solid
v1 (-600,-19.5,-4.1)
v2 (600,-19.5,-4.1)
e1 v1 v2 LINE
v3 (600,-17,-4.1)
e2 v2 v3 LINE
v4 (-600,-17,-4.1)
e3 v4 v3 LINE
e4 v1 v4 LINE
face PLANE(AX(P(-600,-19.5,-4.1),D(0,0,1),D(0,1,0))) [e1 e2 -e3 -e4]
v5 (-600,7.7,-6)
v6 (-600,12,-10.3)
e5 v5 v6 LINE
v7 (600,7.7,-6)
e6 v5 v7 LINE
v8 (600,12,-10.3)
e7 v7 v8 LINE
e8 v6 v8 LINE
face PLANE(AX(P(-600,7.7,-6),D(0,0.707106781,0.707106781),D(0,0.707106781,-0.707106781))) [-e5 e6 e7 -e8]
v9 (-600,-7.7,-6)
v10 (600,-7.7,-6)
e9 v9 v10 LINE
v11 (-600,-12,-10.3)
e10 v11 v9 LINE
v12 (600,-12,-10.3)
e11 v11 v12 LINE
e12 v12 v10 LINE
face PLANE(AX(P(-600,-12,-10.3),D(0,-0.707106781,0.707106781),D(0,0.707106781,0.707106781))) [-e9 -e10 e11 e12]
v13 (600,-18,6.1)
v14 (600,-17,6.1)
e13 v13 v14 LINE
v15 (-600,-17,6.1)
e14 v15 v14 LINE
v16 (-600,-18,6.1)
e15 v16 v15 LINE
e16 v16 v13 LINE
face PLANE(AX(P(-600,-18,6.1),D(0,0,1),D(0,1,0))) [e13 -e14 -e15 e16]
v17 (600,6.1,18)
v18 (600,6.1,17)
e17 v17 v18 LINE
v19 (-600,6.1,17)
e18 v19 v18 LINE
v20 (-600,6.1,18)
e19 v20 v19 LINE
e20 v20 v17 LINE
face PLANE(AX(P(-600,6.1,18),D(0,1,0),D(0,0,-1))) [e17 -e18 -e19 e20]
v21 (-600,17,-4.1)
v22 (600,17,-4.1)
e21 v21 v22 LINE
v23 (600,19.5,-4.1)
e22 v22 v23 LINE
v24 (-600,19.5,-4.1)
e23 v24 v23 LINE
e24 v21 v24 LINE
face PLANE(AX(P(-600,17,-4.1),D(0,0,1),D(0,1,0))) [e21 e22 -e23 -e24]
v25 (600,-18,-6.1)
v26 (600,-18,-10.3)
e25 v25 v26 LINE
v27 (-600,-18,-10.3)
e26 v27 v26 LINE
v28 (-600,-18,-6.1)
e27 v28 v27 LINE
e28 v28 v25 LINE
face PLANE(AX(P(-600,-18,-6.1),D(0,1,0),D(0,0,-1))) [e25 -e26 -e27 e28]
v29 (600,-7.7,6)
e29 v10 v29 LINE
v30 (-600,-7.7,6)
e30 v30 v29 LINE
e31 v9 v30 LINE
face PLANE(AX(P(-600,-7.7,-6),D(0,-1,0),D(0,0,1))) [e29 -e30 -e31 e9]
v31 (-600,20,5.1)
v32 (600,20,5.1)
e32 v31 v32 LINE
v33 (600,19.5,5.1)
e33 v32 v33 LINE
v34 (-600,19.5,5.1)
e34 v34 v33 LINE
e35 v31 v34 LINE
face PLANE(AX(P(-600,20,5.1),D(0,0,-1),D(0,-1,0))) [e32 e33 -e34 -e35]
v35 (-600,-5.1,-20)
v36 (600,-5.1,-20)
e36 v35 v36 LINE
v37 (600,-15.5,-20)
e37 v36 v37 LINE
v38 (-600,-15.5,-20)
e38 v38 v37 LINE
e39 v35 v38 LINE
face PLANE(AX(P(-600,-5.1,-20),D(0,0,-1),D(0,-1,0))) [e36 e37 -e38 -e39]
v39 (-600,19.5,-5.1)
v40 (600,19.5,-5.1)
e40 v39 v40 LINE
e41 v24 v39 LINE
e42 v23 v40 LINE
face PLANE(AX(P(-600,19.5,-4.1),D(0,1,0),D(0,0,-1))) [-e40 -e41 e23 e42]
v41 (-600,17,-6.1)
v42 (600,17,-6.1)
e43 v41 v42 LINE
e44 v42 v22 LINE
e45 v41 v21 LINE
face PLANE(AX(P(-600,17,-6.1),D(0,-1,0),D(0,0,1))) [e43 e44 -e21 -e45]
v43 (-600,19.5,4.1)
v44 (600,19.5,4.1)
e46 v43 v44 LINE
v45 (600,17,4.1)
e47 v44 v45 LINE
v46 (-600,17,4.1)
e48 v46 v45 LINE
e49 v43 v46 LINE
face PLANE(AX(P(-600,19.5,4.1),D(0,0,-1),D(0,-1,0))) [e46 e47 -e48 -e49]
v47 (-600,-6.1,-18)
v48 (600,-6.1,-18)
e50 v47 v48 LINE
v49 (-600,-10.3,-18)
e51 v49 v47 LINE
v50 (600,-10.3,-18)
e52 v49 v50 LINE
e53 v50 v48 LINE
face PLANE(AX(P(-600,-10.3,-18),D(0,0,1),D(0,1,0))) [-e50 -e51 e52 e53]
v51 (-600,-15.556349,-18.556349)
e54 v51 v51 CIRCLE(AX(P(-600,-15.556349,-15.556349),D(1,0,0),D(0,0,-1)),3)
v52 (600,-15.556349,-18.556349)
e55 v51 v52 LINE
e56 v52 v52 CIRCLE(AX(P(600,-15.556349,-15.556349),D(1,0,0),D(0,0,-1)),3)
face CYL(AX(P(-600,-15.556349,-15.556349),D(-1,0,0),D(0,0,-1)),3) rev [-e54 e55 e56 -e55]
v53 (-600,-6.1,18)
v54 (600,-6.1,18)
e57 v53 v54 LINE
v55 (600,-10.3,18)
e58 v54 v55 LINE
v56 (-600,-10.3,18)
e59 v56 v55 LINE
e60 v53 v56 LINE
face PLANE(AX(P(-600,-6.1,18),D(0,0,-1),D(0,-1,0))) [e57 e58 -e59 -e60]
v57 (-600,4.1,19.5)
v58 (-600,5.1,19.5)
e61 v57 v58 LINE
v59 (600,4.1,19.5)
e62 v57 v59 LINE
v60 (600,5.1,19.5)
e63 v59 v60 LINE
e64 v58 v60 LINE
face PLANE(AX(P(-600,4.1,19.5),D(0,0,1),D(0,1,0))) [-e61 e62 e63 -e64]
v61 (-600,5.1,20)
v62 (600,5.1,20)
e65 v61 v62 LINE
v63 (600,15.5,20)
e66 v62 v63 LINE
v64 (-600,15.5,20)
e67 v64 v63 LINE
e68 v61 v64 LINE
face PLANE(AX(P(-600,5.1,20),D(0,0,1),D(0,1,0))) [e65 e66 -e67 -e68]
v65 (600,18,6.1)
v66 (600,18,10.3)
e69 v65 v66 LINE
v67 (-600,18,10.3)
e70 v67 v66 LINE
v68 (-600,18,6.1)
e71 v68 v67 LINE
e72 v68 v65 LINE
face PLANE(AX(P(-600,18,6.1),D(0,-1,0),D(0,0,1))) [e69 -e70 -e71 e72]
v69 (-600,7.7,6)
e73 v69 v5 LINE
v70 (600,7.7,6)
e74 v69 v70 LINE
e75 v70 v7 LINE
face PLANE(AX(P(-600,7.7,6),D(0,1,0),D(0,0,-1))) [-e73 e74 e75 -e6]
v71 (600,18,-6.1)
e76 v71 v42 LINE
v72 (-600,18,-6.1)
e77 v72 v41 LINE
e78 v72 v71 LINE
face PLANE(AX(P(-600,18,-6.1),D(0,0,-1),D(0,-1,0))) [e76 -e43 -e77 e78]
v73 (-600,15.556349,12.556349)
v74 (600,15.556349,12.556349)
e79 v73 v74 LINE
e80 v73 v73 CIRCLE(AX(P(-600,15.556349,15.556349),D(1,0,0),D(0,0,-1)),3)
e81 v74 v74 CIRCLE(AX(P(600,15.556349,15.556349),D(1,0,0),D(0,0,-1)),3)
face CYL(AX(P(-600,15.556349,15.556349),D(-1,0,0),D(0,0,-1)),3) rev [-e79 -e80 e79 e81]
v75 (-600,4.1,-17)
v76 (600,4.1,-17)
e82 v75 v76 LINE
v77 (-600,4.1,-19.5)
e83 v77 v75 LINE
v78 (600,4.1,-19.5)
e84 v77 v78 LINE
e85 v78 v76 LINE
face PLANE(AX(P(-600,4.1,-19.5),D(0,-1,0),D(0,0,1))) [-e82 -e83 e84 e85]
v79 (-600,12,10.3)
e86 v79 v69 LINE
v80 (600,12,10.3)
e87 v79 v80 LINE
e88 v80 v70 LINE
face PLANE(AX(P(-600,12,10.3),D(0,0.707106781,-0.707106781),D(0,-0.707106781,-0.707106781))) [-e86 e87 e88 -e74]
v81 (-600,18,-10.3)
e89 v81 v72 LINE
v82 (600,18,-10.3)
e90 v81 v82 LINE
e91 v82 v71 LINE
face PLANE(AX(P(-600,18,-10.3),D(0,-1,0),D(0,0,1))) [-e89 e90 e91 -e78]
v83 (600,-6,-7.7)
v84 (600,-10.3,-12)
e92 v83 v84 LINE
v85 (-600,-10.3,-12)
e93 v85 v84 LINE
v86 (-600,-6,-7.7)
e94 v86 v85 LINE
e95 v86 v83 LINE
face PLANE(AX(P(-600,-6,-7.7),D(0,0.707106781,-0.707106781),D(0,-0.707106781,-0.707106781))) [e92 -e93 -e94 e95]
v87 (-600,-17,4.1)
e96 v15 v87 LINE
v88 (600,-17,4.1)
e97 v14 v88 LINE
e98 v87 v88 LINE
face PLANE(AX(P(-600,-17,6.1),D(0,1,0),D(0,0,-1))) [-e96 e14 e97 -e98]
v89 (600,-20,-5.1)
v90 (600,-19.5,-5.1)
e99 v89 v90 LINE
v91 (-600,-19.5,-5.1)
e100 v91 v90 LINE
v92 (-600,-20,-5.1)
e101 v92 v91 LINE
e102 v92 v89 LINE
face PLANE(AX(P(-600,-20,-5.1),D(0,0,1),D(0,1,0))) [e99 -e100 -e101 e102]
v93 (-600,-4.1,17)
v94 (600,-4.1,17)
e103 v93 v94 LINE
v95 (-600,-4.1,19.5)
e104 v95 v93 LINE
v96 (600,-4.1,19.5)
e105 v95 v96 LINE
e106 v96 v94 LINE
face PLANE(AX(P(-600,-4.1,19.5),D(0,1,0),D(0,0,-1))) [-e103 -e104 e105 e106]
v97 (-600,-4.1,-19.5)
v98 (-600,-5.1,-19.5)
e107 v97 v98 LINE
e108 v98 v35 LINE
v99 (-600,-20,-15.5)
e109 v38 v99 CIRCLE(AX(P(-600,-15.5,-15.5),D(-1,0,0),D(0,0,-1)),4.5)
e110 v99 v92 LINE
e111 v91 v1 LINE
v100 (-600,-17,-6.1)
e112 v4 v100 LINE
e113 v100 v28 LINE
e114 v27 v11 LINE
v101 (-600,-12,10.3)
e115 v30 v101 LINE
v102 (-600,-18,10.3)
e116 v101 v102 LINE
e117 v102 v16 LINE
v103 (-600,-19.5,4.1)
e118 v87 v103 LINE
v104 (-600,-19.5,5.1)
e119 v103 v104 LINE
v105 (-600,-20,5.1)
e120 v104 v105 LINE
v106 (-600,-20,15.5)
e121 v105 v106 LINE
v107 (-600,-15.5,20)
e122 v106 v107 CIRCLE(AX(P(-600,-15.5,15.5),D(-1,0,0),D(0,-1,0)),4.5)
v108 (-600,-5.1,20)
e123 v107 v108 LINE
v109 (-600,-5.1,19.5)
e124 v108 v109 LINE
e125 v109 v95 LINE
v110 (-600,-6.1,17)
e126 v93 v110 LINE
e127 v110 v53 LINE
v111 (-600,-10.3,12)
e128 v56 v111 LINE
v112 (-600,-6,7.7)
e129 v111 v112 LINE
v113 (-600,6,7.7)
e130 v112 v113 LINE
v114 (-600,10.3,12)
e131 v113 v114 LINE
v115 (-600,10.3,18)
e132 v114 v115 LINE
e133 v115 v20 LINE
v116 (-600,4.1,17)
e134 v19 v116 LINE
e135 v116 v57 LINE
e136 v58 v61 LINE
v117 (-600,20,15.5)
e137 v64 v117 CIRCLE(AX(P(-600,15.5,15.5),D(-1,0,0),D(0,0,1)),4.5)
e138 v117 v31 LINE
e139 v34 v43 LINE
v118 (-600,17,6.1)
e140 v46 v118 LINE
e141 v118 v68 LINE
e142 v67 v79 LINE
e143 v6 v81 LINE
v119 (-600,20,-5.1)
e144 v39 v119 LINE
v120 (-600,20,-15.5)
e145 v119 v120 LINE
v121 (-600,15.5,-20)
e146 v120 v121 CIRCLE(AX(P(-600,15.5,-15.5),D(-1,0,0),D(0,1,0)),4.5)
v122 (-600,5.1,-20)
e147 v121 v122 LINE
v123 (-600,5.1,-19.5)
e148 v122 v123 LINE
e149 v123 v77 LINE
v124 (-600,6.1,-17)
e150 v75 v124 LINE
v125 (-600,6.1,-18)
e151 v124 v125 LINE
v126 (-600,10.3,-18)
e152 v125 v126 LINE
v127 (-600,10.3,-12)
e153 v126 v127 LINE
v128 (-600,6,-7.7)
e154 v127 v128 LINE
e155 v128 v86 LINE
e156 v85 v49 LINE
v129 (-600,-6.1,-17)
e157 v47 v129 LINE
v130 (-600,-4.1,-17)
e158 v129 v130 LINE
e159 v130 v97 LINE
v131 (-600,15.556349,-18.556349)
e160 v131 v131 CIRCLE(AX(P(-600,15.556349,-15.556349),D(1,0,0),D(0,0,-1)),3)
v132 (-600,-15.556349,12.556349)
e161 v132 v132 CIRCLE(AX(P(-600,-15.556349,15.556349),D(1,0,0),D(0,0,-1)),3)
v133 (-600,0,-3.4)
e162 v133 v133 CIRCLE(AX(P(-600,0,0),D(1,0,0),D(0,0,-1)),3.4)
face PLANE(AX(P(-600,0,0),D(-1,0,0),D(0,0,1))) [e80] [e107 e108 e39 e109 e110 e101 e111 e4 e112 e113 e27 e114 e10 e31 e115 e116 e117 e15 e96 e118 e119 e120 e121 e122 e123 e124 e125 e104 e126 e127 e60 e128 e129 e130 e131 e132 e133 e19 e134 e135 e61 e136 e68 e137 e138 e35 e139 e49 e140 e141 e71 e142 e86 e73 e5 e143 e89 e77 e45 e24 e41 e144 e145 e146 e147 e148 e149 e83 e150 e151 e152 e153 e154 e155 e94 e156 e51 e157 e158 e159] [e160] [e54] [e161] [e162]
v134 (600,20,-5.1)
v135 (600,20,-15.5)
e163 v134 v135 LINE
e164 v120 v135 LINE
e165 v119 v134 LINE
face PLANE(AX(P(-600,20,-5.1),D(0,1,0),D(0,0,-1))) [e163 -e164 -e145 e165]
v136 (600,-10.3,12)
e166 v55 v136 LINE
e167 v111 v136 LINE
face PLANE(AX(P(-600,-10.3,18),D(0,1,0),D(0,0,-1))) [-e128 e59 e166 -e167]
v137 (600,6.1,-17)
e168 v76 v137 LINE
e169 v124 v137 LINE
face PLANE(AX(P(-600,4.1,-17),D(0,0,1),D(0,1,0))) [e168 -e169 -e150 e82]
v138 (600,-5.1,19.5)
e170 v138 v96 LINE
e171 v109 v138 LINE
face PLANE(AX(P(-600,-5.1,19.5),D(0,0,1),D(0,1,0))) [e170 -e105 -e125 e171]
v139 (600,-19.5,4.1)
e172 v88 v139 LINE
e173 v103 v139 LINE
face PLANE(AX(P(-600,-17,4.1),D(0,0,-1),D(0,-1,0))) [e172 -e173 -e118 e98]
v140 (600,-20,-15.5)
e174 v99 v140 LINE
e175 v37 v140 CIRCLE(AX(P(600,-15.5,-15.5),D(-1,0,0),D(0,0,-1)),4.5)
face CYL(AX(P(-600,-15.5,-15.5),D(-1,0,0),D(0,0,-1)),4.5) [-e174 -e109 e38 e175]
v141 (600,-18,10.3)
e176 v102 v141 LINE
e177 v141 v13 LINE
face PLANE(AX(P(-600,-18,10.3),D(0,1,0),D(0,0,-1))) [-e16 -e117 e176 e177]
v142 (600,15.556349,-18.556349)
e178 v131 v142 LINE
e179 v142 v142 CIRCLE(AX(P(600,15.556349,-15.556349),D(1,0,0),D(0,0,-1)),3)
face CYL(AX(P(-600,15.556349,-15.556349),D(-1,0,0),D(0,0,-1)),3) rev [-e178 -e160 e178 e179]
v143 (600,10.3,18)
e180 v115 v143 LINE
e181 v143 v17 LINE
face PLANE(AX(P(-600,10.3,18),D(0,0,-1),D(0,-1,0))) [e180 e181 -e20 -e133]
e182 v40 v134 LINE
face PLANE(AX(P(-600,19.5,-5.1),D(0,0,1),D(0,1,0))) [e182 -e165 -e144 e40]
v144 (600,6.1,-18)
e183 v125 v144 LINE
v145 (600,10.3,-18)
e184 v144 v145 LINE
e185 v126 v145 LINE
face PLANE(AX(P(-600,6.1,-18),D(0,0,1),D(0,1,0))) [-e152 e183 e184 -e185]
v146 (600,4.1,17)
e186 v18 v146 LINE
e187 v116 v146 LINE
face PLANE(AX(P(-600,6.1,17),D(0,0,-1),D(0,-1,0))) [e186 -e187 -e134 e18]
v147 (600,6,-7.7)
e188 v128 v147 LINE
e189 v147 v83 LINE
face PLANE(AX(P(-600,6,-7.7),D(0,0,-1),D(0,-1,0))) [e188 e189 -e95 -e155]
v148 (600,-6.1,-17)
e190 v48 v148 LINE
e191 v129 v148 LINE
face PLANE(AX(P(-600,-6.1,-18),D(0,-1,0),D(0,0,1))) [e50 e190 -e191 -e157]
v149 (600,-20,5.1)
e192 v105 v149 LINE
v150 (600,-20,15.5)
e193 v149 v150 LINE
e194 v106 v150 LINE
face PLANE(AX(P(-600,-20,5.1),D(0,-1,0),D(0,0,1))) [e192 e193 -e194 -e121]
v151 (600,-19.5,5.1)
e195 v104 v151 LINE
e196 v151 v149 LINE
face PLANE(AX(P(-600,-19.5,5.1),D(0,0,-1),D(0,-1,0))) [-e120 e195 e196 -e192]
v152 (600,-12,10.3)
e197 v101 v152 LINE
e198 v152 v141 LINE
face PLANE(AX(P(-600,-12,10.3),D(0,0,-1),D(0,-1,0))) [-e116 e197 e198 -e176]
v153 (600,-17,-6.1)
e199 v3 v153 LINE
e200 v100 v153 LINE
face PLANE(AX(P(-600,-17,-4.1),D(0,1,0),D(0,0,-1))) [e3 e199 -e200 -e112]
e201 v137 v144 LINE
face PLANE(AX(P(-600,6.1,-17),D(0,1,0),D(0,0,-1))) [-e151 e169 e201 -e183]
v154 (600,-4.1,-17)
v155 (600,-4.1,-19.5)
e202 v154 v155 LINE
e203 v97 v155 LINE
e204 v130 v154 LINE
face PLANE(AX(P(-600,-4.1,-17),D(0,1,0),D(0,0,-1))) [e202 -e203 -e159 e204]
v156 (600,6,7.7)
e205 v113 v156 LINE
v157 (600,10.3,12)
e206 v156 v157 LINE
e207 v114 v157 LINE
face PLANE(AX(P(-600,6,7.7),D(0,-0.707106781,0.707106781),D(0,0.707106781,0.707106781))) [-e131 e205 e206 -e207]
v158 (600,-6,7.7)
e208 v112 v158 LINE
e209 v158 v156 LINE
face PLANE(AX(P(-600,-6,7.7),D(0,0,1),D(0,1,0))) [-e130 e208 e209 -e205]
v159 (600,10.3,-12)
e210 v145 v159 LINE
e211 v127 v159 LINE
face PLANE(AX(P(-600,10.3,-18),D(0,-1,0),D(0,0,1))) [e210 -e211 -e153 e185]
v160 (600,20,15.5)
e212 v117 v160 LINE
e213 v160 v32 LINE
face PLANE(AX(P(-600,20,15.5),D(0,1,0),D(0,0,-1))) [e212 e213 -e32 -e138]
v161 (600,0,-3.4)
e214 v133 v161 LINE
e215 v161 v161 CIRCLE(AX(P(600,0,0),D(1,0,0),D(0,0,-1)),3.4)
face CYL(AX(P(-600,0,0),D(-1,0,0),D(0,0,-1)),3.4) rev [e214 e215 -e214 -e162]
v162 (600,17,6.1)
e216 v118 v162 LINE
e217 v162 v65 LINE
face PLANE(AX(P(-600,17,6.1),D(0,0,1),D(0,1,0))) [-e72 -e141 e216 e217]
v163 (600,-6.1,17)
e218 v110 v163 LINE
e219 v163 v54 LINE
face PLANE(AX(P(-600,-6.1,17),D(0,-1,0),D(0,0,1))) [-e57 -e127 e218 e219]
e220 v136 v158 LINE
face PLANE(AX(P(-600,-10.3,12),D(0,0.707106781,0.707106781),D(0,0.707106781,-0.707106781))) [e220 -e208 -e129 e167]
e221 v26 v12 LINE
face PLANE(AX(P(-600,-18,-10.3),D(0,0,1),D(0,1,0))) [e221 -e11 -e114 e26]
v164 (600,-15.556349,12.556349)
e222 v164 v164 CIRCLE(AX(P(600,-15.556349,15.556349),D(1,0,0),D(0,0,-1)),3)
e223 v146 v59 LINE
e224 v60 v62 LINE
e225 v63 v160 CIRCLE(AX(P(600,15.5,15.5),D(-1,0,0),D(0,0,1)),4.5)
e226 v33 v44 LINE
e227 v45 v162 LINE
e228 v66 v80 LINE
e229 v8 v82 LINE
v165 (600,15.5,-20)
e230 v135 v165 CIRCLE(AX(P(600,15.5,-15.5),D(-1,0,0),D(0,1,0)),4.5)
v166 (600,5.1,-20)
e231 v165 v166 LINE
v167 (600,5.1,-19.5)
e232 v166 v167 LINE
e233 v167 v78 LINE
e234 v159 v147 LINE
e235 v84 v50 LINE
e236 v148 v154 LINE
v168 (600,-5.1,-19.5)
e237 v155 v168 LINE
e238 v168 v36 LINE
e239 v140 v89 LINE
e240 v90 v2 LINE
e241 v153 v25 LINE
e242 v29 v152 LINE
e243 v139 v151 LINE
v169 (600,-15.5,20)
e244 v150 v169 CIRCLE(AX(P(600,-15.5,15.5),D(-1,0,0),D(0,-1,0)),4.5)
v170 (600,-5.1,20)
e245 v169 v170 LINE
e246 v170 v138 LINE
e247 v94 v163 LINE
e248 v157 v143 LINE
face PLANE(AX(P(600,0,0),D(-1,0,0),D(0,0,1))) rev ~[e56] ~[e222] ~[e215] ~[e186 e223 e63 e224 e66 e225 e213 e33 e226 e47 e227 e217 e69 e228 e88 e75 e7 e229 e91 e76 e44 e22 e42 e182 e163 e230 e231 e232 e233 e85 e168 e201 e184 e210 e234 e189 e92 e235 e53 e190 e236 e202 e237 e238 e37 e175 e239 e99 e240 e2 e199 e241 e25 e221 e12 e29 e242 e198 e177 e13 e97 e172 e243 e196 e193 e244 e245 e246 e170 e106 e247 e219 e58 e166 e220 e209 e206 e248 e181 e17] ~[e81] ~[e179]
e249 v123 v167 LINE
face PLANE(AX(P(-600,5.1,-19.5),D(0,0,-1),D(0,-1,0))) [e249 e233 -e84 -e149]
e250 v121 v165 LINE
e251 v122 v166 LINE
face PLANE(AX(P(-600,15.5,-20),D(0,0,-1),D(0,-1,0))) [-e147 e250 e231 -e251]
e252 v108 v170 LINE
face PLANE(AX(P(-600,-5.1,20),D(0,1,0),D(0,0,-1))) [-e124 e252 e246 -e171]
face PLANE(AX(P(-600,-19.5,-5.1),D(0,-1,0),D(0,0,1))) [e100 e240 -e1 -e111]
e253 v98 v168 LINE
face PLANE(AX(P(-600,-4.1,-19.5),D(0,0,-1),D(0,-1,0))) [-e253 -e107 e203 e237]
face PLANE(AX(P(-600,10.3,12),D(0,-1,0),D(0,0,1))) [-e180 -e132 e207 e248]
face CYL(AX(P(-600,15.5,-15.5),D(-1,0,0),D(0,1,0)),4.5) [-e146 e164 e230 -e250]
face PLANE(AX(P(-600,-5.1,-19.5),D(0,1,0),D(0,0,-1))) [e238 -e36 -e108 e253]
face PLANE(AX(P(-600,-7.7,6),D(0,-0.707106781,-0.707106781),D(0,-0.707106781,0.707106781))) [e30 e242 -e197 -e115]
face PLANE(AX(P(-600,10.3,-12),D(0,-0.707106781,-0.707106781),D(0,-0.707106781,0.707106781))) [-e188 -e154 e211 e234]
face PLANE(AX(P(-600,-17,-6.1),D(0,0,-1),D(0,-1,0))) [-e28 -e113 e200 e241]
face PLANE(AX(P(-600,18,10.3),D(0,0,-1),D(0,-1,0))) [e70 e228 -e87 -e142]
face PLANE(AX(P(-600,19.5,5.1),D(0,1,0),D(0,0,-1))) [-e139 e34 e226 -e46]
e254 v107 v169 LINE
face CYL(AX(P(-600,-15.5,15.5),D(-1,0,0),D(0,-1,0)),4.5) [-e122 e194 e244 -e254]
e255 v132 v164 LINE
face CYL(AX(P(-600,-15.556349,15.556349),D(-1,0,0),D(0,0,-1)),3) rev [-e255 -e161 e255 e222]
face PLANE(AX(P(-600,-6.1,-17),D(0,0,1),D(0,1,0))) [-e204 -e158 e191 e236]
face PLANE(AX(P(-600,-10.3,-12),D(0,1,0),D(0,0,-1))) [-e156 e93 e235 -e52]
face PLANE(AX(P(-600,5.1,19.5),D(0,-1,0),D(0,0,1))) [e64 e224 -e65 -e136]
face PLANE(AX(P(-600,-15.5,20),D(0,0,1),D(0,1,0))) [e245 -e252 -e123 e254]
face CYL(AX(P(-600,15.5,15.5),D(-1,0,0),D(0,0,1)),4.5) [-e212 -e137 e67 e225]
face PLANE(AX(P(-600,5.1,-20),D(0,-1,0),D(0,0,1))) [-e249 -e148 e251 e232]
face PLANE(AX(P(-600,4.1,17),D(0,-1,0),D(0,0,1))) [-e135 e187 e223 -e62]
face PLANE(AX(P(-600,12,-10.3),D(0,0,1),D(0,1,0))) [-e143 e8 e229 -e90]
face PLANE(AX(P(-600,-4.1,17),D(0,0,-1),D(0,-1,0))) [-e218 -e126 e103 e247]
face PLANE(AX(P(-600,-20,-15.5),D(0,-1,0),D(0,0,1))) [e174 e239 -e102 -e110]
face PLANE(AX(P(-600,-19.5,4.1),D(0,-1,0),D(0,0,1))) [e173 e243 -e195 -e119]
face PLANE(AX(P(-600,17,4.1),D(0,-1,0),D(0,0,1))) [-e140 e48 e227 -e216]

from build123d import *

# Parameters (mm, degrees)
SKETCH1_R                 = 3.4
SKETCH1_R_2               = 3
F_40_X_40W_X_R4_5_1_DEPTH = 1200


with BuildPart() as part:
    # Sketch1 → 铝型材 40 X 40W X R4.5(1) (new body)
    with BuildSketch(Plane(origin=(-600, 0, 0), x_dir=(0, 0, -1), z_dir=(1, 0, 0))):
        with BuildLine():
            Line((-5.1, 20), (-5.1, 19.5))
            Line((-5.1, 19.5), (-4.1, 19.5))
            Line((-4.1, 19.5), (-4.1, 17))
            Line((-4.1, 17), (-6.1, 17))
            Line((-6.1, 17), (-6.1, 18))
            Line((-6.1, 18), (-10.3, 18))
            Line((-10.3, 18), (-10.3, 12))
            Line((-10.3, 12), (-6, 7.7))
            Line((-6, 7.7), (6, 7.7))
            Line((6, 7.7), (10.3, 12))
            Line((10.3, 12), (10.3, 18))
            Line((10.3, 18), (6.1, 18))
            Line((6.1, 18), (6.1, 17))
            Line((6.1, 17), (4.1, 17))
            Line((4.1, 17), (4.1, 19.5))
            Line((4.1, 19.5), (5.1, 19.5))
            Line((5.1, 19.5), (5.1, 20))
            Line((5.1, 20), (15.5, 20))
            ThreePointArc((15.5, 20), (18.681980515, 18.681980515), (20, 15.5))
            Line((20, 15.5), (20, 5.1))
            Line((20, 5.1), (19.5, 5.1))
            Line((19.5, 5.1), (19.5, 4.1))
            Line((19.5, 4.1), (17, 4.1))
            Line((17, 4.1), (17, 6.1))
            Line((17, 6.1), (18, 6.1))
            Line((18, 6.1), (18, 10.3))
            Line((18, 10.3), (12, 10.3))
            Line((12, 10.3), (7.7, 6))
            Line((7.7, 6), (7.7, -6))
            Line((7.7, -6), (12, -10.3))
            Line((12, -10.3), (18, -10.3))
            Line((18, -10.3), (18, -6.1))
            Line((18, -6.1), (17, -6.1))
            Line((17, -6.1), (17, -4.1))
            Line((17, -4.1), (19.5, -4.1))
            Line((19.5, -4.1), (19.5, -5.1))
            Line((19.5, -5.1), (20, -5.1))
            Line((20, -5.1), (20, -15.5))
            ThreePointArc((20, -15.5), (18.681980515, -18.681980515), (15.5, -20))
            Line((15.5, -20), (5.1, -20))
            Line((5.1, -20), (5.1, -19.5))
            Line((5.1, -19.5), (4.1, -19.5))
            Line((4.1, -19.5), (4.1, -17))
            Line((4.1, -17), (6.1, -17))
            Line((6.1, -17), (6.1, -18))
            Line((6.1, -18), (10.3, -18))
            Line((10.3, -18), (10.3, -12))
            Line((10.3, -12), (6, -7.7))
            Line((6, -7.7), (-6, -7.7))
            Line((-6, -7.7), (-10.3, -12))
            Line((-10.3, -12), (-10.3, -18))
            Line((-10.3, -18), (-6.1, -18))
            Line((-6.1, -18), (-6.1, -17))
            Line((-6.1, -17), (-4.1, -17))
            Line((-4.1, -17), (-4.1, -19.5))
            Line((-4.1, -19.5), (-5.1, -19.5))
            Line((-5.1, -19.5), (-5.1, -20))
            Line((-5.1, -20), (-15.5, -20))
            ThreePointArc((-15.5, -20), (-18.681980515, -18.681980515), (-20, -15.5))
            Line((-20, -15.5), (-20, -5.1))
            Line((-20, -5.1), (-19.5, -5.1))
            Line((-19.5, -5.1), (-19.5, -4.1))
            Line((-19.5, -4.1), (-17, -4.1))
            Line((-17, -4.1), (-17, -6.1))
            Line((-17, -6.1), (-18, -6.1))
            Line((-18, -6.1), (-18, -10.3))
            Line((-18, -10.3), (-12, -10.3))
            Line((-12, -10.3), (-7.7, -6))
            Line((-7.7, -6), (-7.7, 6))
            Line((-7.7, 6), (-12, 10.3))
            Line((-12, 10.3), (-18, 10.3))
            Line((-18, 10.3), (-18, 6.1))
            Line((-18, 6.1), (-17, 6.1))
            Line((-17, 6.1), (-17, 4.1))
            Line((-17, 4.1), (-19.5, 4.1))
            Line((-19.5, 4.1), (-19.5, 5.1))
            Line((-19.5, 5.1), (-20, 5.1))
            Line((-20, 5.1), (-20, 15.5))
            ThreePointArc((-20, 15.5), (-18.681980515, 18.681980515), (-15.5, 20))
            Line((-15.5, 20), (-5.1, 20))
        make_face()
        Circle(SKETCH1_R, mode=Mode.SUBTRACT)
        with Locations((-15.556349186, 15.556349186)):
            Circle(SKETCH1_R_2, mode=Mode.SUBTRACT)
        with Locations((15.556349186, 15.556349186)):
            Circle(SKETCH1_R_2, mode=Mode.SUBTRACT)
        with Locations((15.556349186, -15.556349186)):
            Circle(SKETCH1_R_2, mode=Mode.SUBTRACT)
        with Locations((-15.556349186, -15.556349186)):
            Circle(SKETCH1_R_2, mode=Mode.SUBTRACT)
    extrude(amount=F_40_X_40W_X_R4_5_1_DEPTH)


solid = part.part
